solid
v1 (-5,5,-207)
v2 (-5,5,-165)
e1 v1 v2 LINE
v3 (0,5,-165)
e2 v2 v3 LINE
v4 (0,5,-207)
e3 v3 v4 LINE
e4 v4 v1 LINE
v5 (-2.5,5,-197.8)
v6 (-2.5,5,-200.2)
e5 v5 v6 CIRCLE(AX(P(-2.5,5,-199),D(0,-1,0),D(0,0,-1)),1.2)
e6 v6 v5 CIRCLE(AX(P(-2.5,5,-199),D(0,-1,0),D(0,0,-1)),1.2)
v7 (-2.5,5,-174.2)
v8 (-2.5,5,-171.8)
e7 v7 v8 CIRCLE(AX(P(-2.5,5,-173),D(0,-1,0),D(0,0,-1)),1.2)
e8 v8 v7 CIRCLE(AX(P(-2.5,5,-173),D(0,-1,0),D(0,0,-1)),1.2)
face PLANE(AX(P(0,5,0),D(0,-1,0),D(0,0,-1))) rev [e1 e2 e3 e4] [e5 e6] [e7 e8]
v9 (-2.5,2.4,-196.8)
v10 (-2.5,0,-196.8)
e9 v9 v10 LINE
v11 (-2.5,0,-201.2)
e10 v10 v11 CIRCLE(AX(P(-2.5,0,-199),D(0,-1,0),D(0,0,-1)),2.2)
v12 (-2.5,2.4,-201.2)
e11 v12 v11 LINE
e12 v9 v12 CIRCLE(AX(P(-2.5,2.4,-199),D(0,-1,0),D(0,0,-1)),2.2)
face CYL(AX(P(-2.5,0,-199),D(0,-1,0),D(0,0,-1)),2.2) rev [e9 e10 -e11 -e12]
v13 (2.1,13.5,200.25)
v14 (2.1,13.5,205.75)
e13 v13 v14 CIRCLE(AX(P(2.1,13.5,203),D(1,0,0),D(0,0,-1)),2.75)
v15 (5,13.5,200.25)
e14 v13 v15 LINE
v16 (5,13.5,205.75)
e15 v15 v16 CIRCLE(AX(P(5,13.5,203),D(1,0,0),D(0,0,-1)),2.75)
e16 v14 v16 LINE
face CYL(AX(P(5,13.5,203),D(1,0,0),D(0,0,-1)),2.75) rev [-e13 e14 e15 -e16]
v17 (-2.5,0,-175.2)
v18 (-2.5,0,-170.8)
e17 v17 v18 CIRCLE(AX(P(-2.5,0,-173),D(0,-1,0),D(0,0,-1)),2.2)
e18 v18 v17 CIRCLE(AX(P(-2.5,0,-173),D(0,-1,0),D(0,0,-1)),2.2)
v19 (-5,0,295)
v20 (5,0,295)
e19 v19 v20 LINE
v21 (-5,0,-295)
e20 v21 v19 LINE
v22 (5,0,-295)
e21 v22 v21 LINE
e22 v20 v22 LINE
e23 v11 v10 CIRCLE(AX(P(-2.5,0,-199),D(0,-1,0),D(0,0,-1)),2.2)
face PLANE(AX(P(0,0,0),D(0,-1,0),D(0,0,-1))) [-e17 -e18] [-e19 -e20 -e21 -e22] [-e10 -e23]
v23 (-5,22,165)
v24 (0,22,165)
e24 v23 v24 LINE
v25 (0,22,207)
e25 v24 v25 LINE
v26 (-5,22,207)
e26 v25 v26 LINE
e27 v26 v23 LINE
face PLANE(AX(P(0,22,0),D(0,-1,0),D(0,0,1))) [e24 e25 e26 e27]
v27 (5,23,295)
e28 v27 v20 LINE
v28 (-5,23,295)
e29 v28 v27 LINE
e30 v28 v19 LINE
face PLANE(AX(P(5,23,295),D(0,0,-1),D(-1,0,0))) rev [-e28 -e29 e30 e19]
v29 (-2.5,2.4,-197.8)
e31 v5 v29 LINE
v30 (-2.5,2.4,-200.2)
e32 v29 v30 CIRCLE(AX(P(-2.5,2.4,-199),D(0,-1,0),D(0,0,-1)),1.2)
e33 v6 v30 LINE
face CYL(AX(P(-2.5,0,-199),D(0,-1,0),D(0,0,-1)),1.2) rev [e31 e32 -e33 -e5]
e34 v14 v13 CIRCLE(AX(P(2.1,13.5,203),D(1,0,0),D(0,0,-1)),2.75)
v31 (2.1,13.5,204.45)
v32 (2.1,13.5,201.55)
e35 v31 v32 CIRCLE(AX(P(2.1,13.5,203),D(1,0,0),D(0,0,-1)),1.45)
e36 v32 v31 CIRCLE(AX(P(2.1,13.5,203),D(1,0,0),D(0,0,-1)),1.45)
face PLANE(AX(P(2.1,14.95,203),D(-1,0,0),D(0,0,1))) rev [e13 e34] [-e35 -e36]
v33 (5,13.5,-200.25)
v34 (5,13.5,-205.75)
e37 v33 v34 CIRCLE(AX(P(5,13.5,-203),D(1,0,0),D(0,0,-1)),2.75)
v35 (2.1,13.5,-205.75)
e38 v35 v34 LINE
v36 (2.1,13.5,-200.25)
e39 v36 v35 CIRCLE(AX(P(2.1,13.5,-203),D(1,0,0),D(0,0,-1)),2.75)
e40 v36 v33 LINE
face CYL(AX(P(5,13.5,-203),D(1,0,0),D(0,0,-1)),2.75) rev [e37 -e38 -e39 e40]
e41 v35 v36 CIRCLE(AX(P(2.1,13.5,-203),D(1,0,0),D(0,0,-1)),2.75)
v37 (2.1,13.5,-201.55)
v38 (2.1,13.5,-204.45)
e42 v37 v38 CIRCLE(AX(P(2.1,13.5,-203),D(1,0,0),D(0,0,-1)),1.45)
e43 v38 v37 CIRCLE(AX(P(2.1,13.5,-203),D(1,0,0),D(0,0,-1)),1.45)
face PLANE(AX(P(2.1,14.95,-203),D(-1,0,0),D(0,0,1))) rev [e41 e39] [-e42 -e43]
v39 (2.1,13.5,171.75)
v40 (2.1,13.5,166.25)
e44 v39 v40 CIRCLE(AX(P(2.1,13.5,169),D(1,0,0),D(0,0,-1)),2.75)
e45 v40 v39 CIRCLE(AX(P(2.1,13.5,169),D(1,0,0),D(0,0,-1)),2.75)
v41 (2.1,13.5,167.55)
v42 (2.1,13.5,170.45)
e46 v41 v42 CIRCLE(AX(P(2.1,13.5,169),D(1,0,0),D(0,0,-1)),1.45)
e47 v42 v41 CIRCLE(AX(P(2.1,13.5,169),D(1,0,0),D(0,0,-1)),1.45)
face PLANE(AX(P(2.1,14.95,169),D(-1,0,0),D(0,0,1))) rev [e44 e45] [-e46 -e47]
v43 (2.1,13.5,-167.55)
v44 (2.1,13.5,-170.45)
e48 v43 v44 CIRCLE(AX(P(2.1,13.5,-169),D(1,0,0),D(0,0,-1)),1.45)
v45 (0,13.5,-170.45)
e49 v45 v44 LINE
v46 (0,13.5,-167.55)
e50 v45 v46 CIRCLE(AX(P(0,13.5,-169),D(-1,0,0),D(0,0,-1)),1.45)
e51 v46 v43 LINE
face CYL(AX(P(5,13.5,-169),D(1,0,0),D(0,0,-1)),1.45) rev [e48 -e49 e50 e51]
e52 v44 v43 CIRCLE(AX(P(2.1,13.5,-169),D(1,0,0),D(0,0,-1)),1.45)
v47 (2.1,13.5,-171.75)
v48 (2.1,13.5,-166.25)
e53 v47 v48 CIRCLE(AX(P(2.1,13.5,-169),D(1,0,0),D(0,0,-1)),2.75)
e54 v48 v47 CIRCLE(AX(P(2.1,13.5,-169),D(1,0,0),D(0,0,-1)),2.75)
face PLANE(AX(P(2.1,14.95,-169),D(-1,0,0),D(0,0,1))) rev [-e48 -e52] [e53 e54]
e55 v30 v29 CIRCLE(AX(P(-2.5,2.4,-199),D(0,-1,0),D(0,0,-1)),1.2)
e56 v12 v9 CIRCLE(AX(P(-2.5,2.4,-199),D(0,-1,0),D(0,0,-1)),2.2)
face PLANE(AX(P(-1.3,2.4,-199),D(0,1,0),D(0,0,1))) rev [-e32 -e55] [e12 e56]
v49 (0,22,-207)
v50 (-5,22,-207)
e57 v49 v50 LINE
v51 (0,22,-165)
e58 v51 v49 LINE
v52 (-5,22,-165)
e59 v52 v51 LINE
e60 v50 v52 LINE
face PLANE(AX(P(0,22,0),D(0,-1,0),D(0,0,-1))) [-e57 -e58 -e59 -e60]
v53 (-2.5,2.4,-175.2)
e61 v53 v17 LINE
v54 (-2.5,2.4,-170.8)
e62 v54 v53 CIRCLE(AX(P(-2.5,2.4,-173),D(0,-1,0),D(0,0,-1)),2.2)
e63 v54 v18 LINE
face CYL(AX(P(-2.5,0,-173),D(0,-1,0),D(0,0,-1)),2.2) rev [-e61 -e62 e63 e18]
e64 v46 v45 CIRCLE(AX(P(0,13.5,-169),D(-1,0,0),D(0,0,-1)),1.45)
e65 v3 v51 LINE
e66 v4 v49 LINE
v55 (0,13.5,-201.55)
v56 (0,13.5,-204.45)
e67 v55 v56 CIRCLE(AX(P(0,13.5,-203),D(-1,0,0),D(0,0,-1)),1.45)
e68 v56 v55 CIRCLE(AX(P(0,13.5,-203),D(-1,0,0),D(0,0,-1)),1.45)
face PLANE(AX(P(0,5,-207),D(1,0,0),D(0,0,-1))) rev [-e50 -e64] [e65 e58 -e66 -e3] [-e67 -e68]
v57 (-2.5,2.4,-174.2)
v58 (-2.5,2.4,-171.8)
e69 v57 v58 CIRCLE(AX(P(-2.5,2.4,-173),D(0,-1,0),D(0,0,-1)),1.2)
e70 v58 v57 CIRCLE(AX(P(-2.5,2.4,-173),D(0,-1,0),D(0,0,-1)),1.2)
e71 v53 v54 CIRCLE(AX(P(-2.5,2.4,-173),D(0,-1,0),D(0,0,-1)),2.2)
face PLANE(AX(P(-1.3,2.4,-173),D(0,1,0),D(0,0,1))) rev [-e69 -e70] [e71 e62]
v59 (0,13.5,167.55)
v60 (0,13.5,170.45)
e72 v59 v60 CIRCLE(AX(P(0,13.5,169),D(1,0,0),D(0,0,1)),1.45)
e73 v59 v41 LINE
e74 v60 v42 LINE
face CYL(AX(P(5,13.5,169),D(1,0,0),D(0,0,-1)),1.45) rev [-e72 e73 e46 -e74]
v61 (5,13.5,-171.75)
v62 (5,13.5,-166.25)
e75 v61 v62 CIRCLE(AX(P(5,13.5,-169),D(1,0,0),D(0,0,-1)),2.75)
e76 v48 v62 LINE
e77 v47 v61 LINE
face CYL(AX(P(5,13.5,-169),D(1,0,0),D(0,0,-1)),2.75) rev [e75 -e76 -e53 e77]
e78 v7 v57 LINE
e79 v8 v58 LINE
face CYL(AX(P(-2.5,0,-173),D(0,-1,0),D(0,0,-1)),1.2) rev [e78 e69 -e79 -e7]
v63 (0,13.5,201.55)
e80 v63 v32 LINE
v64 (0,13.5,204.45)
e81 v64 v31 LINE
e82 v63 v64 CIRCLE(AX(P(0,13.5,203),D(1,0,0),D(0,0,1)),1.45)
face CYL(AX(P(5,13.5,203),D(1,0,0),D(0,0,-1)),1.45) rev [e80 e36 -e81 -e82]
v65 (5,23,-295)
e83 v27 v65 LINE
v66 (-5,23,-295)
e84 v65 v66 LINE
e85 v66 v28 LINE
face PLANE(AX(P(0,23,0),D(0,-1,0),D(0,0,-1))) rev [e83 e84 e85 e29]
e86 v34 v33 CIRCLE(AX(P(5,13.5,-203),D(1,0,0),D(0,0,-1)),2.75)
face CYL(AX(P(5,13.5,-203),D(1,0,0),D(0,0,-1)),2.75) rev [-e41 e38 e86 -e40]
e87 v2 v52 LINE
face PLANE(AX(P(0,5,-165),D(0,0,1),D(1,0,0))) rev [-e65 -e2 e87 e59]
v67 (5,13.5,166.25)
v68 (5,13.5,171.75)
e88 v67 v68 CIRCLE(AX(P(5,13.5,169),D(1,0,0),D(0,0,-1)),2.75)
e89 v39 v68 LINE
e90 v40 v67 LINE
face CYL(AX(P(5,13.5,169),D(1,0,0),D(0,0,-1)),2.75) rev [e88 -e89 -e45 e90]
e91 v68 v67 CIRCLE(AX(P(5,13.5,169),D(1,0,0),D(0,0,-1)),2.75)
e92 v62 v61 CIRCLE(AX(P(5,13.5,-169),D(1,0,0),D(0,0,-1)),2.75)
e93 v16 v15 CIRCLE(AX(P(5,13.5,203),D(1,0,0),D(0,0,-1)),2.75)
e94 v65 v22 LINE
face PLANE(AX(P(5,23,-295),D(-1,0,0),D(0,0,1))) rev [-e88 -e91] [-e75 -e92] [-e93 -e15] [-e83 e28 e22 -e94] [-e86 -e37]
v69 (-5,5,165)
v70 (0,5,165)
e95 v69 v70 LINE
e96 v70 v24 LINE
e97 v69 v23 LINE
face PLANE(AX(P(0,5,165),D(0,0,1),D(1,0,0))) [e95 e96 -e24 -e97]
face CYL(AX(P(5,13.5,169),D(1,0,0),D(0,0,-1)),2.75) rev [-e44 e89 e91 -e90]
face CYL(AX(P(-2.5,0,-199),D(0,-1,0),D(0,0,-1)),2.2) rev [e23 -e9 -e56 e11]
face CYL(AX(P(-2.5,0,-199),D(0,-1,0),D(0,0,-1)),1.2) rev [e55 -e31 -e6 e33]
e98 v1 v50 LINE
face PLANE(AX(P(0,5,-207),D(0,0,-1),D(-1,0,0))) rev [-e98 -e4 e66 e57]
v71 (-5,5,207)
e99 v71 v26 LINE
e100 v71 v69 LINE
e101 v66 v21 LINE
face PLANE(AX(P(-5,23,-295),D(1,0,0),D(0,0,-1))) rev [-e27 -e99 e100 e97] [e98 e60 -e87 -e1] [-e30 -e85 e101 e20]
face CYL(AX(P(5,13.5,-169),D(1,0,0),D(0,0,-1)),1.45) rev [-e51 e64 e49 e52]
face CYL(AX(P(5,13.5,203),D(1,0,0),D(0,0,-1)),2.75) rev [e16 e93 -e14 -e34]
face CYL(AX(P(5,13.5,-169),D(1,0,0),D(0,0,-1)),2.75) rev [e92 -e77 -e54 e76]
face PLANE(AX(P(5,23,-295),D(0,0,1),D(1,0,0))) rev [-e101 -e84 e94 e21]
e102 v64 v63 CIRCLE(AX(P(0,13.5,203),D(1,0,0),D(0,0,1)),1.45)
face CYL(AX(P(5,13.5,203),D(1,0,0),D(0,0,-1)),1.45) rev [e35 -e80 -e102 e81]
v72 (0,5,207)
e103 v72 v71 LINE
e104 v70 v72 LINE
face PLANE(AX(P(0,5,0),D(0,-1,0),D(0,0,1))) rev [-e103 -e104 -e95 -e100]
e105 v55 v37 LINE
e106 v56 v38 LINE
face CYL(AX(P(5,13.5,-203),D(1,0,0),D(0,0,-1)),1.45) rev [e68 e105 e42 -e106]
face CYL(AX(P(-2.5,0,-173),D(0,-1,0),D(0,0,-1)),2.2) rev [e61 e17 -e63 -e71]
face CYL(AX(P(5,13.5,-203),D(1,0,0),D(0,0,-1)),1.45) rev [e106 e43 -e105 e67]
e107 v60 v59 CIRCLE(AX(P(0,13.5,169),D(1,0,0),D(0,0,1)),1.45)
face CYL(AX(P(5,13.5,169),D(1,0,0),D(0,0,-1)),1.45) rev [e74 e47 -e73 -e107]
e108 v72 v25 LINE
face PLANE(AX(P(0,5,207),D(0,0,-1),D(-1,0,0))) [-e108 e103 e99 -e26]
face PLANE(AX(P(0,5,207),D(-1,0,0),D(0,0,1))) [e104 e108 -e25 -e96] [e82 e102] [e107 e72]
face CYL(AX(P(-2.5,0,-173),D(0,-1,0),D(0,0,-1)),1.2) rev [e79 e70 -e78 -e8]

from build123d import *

# Parameters (mm, degrees)
SKETCH1_W                                    = 10
SKETCH1_H                                    = 590
BOSS_EXTRUDE1_DEPTH                          = 23
CBORE_FOR_M2_5_HEX_SOCKET_HEAD_CAP_S_2_COUNT = 2
CBORE_FOR_M2_5_HEX_SOCKET_HEAD_CAP_S_2_PITCH = 34
CUT_EXTRUDE1_START                           = -1
SKETCH10_W                                   = 5
SKETCH10_H                                   = 42
CUT_EXTRUDE1_DEPTH                           = 17
CBORE_FOR_M2_HEX_SOCKET_HEAD_CAP_SCR_3_COUNT = 2
CBORE_FOR_M2_HEX_SOCKET_HEAD_CAP_SCR_3_PITCH = 26


with BuildPart() as part:
    # Sketch1 → Boss-Extrude1 (new body)
    with BuildSketch(Plane(origin=(0, 0, 0), x_dir=(1, 0, 0), z_dir=(0, 1, 0))):
        Rectangle(SKETCH1_W, SKETCH1_H)
    extrude(amount=BOSS_EXTRUDE1_DEPTH)

    # Sketch9 → CBORE for M2.5 Hex Socket Head Cap Screw1 (revolve, cut)
    with BuildSketch(Plane(origin=(5, 13.5, 203), x_dir=(0, 0, -1), z_dir=(0, 1, 0))):
        Polygon((0, 0), (0, 22.811247898), (1.45, 21.94), (1.45, 2.9), (2.75, 2.9), (2.75, 0), align=None)
    cbore_for_m2_5_hex_socket_head_cap_screw = revolve(axis=Axis((11.35, 13.5, 203), (-1, 0, 0)), mode=Mode.SUBTRACT)

    # CBORE for M2.5 Hex Socket Head Cap S 2: CBORE for M2.5 Hex Socket Head Cap Screw1 ×2
    with Locations(*[(0, 0, -i * CBORE_FOR_M2_5_HEX_SOCKET_HEAD_CAP_S_2_PITCH) for i in range(1, CBORE_FOR_M2_5_HEX_SOCKET_HEAD_CAP_S_2_COUNT)]):
        add(cbore_for_m2_5_hex_socket_head_cap_screw, mode=Mode.SUBTRACT)

    # Mirror1: CBORE for M2.5 Hex Socket Head Cap Screw1 across plane
    add(cbore_for_m2_5_hex_socket_head_cap_screw.mirror(Plane.XY), mode=Mode.SUBTRACT)

    # Mirror1 copy 1 sketch → Mirror1 copy 1 (revolve, cut)
    with BuildSketch(Plane(origin=(5, 13.5, -169), x_dir=(0, 0, 1), z_dir=(0, 1, 0))):
        Polygon((0, 0), (0, -22.811247898), (1.45, -21.94), (1.45, -2.9), (2.75, -2.9), (2.75, 0), align=None)
    revolve(axis=Axis((11.35, 13.5, -169), (1, 0, 0)), mode=Mode.SUBTRACT)

    # Sketch10 → Cut-Extrude1 (cut)
    with BuildSketch(Plane(origin=(0, 23, 0), x_dir=(1, 0, 0), z_dir=(0, 1, 0)).offset(CUT_EXTRUDE1_START)):
        with Locations((-2.5, 186)):
            Rectangle(SKETCH10_W, SKETCH10_H)
    cut_extrude1 = extrude(amount=-CUT_EXTRUDE1_DEPTH, mode=Mode.SUBTRACT)

    # Mirror2: Cut-Extrude1 across plane
    add(cut_extrude1.mirror(Plane.XY), mode=Mode.SUBTRACT)

    # Sketch12 → CBORE for M2 Hex Socket Head Cap Screw1 (revolve, cut)
    with BuildSketch(Plane(origin=(-2.5, 0, -173), x_dir=(0, 0, -1), z_dir=(1, 0, 0))):
        Polygon((0, 0), (0, 20.721032743), (1.2, 20), (1.2, 2.4), (2.2, 2.4), (2.2, 0), align=None)
    cbore_for_m2_hex_socket_head_cap_screw1 = revolve(axis=Axis((-2.5, -6.35, -173), (0, 1, 0)), mode=Mode.SUBTRACT)

    # CBORE for M2 Hex Socket Head Cap Scr 3: CBORE for M2 Hex Socket Head Cap Screw1 ×2
    with Locations(*[(0, 0, -i * CBORE_FOR_M2_HEX_SOCKET_HEAD_CAP_SCR_3_PITCH) for i in range(1, CBORE_FOR_M2_HEX_SOCKET_HEAD_CAP_SCR_3_COUNT)]):
        add(cbore_for_m2_hex_socket_head_cap_screw1, mode=Mode.SUBTRACT)


solid = part.part
